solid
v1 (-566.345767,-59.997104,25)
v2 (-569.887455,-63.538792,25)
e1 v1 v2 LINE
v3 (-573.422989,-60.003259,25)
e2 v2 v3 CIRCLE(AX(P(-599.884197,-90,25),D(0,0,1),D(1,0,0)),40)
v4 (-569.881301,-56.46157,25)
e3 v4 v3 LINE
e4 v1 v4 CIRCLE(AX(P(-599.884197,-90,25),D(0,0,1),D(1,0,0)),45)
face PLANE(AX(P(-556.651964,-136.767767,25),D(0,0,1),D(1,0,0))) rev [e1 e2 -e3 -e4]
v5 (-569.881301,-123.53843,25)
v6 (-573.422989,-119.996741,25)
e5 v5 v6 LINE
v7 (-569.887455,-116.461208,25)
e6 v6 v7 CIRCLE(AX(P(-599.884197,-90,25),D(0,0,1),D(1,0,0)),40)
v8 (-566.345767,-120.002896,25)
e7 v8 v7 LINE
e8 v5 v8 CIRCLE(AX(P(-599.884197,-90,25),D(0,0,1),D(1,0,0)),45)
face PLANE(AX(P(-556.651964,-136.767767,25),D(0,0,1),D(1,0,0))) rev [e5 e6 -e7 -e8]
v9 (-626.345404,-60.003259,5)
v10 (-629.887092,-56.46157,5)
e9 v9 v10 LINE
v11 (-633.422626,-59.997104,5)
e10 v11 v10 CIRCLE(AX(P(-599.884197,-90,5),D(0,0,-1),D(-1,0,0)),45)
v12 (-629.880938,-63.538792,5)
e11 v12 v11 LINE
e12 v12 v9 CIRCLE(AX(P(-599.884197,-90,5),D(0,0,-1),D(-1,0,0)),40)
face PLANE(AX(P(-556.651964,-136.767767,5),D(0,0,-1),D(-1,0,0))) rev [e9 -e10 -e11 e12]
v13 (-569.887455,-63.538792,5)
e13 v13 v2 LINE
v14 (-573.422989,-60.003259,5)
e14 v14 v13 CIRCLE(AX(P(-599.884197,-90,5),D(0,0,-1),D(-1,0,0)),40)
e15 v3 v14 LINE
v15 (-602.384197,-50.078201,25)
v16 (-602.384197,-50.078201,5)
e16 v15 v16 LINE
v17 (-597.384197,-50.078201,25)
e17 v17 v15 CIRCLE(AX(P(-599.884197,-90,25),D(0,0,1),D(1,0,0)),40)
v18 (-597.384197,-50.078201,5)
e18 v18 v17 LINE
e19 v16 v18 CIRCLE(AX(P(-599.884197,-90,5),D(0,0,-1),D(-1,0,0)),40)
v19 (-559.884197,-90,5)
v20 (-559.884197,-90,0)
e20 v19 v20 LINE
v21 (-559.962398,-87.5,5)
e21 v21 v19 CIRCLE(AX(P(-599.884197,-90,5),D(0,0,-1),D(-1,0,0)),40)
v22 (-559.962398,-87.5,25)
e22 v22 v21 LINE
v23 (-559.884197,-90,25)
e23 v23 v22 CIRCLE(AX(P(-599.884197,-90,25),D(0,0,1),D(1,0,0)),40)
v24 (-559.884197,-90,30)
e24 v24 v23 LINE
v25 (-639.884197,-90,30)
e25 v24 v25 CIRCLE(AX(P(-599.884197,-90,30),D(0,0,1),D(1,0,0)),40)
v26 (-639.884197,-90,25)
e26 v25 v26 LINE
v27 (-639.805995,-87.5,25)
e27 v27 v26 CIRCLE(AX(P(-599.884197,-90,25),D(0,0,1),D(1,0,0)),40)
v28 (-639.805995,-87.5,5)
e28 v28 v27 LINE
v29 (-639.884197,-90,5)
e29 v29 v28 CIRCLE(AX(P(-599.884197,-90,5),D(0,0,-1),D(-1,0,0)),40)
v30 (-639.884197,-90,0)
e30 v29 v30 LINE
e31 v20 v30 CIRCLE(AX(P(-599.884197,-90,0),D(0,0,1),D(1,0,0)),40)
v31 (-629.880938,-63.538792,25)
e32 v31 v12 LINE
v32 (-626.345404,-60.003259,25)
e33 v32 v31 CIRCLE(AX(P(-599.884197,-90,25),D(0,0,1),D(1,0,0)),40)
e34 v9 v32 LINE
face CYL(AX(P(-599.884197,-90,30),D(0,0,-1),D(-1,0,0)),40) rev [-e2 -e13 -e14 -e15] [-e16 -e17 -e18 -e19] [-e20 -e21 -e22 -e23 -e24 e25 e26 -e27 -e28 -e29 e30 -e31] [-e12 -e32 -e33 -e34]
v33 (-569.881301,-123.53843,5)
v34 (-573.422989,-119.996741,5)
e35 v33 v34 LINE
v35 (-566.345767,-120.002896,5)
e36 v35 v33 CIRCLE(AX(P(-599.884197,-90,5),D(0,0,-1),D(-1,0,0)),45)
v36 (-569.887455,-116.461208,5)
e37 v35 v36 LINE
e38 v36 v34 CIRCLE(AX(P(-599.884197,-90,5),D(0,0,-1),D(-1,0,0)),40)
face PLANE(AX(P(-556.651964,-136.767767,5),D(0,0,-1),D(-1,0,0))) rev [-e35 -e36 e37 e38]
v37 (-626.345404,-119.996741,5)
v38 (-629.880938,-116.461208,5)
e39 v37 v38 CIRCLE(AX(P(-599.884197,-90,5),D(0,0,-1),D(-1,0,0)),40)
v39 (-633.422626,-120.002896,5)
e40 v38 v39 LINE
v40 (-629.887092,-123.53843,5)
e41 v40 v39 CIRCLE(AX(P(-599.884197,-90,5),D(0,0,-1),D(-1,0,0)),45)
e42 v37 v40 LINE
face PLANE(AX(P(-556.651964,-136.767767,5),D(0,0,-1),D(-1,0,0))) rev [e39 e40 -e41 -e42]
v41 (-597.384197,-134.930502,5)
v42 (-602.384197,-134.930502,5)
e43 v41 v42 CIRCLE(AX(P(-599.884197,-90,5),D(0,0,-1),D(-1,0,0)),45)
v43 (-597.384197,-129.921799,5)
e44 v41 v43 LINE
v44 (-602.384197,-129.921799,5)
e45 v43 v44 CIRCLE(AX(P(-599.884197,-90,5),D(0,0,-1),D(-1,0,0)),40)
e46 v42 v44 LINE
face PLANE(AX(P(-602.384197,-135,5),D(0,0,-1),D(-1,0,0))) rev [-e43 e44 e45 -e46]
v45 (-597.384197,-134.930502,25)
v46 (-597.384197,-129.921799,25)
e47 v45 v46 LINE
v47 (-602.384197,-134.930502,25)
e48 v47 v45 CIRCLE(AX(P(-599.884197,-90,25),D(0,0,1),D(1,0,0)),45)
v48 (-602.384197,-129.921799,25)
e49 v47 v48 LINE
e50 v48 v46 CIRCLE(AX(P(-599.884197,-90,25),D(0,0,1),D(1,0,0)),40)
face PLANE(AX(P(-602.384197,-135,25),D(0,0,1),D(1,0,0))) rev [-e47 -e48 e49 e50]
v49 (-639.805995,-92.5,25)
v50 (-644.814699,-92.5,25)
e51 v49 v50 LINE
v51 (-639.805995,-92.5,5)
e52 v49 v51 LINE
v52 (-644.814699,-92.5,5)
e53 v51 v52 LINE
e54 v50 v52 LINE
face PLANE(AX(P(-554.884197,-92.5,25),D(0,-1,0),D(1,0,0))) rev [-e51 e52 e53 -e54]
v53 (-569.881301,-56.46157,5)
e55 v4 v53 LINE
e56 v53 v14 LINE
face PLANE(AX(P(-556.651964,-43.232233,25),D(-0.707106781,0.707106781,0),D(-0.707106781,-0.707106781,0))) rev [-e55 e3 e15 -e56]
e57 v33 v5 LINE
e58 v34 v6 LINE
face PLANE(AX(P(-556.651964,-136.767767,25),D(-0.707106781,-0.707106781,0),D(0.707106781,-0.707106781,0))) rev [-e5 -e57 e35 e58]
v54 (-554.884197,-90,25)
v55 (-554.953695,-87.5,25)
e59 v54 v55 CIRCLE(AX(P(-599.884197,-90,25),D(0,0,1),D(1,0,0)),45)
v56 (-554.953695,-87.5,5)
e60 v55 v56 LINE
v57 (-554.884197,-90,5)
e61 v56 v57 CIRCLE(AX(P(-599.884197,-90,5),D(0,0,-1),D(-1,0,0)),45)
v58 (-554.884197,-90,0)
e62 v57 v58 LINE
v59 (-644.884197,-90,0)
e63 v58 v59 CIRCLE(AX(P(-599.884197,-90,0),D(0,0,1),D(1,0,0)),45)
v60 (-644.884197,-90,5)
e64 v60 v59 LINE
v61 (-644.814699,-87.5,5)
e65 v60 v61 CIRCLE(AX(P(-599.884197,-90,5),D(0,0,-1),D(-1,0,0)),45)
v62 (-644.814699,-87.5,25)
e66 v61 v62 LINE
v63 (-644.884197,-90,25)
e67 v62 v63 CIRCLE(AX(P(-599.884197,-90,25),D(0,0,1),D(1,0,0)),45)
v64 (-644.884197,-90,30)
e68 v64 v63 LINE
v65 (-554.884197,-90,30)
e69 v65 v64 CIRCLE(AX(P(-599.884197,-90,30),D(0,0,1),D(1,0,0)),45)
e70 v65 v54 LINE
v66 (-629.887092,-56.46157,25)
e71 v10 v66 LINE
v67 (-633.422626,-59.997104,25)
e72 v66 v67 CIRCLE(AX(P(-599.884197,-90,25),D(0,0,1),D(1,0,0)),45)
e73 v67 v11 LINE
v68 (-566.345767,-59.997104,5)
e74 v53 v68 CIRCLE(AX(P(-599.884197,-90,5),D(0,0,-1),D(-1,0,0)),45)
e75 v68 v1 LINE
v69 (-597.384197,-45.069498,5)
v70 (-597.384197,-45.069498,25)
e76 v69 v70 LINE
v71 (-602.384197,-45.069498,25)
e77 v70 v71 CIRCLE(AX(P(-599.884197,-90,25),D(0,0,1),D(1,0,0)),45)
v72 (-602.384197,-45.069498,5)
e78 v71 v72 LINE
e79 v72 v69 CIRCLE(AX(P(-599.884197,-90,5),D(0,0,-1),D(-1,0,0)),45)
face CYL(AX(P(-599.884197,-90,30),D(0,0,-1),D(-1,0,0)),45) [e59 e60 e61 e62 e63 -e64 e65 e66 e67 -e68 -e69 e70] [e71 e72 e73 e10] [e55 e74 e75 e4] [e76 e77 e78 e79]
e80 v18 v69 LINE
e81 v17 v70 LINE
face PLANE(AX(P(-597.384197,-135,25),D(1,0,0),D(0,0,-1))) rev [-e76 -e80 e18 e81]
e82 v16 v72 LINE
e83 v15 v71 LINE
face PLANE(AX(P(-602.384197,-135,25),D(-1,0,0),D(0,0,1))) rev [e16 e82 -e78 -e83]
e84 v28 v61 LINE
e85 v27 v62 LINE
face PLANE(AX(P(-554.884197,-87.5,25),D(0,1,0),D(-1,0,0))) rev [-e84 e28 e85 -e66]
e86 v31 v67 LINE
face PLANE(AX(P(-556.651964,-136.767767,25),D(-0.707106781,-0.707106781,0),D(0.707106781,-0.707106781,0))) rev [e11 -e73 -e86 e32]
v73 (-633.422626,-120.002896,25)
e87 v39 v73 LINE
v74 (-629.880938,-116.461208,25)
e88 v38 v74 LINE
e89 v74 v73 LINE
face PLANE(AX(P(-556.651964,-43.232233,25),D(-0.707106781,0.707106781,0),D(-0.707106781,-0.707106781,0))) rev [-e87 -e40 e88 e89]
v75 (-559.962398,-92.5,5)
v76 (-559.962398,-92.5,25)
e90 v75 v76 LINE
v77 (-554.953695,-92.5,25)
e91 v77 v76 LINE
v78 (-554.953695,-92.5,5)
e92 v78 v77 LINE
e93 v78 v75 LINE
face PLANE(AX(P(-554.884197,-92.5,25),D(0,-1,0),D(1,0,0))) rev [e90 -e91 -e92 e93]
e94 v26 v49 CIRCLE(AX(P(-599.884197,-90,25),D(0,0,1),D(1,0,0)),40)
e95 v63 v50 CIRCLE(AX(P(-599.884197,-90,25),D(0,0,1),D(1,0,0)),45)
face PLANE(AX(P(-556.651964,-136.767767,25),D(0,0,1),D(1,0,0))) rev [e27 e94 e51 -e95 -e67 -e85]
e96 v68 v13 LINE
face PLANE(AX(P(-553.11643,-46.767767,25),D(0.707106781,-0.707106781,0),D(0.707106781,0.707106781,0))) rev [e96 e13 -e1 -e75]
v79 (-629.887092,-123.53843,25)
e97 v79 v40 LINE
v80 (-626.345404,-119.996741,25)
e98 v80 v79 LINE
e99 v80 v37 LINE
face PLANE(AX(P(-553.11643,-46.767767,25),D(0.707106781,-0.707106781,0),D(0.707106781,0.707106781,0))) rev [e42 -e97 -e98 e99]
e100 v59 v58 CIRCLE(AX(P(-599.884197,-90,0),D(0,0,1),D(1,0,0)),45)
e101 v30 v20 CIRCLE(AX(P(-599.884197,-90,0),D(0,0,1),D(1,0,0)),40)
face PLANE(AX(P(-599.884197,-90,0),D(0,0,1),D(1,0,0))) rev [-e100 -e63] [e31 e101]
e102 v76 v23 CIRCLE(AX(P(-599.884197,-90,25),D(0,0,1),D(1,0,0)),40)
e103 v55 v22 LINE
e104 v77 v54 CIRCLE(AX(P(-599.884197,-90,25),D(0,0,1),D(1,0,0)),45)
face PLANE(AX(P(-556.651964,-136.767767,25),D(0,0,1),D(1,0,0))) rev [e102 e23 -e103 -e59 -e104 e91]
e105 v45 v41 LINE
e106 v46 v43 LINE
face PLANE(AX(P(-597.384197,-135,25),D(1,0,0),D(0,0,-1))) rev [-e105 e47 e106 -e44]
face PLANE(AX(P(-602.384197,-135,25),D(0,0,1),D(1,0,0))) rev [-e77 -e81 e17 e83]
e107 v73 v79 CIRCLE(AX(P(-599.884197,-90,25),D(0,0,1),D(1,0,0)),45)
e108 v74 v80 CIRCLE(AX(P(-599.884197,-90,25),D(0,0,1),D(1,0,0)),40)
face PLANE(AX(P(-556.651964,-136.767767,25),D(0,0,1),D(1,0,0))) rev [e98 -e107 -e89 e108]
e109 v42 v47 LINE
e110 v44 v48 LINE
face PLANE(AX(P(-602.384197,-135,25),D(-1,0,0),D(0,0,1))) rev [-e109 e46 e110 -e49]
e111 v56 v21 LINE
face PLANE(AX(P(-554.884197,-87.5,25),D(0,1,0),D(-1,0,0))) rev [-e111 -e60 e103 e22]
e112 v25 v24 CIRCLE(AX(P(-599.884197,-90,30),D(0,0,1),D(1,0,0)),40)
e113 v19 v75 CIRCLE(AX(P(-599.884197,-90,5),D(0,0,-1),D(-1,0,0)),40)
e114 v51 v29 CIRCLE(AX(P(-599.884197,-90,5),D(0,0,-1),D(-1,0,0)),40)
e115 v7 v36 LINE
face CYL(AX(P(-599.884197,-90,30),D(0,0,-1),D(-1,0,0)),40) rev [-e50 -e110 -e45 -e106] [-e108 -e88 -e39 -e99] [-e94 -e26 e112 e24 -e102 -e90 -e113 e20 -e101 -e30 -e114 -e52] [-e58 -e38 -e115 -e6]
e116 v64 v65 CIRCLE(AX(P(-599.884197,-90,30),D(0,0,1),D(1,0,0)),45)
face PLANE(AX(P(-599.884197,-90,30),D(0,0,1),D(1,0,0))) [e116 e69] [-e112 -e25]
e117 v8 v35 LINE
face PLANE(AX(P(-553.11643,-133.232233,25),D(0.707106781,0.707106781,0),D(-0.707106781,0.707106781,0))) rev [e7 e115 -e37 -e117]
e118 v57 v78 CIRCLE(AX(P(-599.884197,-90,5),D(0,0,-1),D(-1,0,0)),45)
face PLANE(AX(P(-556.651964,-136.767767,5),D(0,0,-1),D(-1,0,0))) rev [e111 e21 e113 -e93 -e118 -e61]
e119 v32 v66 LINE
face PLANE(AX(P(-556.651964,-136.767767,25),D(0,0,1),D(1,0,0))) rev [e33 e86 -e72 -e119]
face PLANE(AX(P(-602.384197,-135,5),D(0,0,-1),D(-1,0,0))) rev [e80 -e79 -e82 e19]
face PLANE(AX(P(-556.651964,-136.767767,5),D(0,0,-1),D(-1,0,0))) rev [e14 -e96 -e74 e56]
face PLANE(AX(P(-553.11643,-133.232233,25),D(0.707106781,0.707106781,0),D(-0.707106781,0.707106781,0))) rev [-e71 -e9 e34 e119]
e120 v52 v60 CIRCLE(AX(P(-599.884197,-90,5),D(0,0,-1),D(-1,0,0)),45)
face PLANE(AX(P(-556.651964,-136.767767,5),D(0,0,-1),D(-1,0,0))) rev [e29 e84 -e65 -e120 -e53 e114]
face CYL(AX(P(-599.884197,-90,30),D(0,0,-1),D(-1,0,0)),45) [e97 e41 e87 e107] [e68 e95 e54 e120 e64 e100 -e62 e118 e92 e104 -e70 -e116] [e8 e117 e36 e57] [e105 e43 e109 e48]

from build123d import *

# Parameters (mm, degrees)
SKETCH1_R           = 45
SKETCH1_R_2         = 40
BOSS_EXTRUDE1_DEPTH = 30
SKETCH2_W           = 5
SKETCH2_H           = 20
CUT_EXTRUDE1_DEPTH  = 660.545773414
CIRPATTERN1_COUNT   = 8


with BuildPart() as part:
    # Sketch1 → Boss-Extrude1 (new body)
    with BuildSketch(Plane.XY):
        with Locations((-599.884196758, -90)):
            Circle(SKETCH1_R)
        with Locations((-599.884196758, -90)):
            Circle(SKETCH1_R_2, mode=Mode.SUBTRACT)
    extrude(amount=BOSS_EXTRUDE1_DEPTH)

    # Sketch2 → Cut-Extrude1 (cut, symmetric)
    with BuildSketch(Plane(origin=(0, 0, 0), x_dir=(1, 0, 0), z_dir=(0, 1, 0))):
        with Locations((-599.884196758, -15)):
            Rectangle(SKETCH2_W, SKETCH2_H)
    cut_extrude1 = extrude(amount=CUT_EXTRUDE1_DEPTH, both=True, mode=Mode.SUBTRACT)

    # CirPattern1: Cut-Extrude1 ×8 about axis
    cirpattern1_axis = Axis((-599.884196758, -90, 0), (0, 0, 1))
    for i in range(1, CIRPATTERN1_COUNT):
        add(cut_extrude1.rotate(cirpattern1_axis, i * 360 / CIRPATTERN1_COUNT), mode=Mode.SUBTRACT)


solid = part.part
